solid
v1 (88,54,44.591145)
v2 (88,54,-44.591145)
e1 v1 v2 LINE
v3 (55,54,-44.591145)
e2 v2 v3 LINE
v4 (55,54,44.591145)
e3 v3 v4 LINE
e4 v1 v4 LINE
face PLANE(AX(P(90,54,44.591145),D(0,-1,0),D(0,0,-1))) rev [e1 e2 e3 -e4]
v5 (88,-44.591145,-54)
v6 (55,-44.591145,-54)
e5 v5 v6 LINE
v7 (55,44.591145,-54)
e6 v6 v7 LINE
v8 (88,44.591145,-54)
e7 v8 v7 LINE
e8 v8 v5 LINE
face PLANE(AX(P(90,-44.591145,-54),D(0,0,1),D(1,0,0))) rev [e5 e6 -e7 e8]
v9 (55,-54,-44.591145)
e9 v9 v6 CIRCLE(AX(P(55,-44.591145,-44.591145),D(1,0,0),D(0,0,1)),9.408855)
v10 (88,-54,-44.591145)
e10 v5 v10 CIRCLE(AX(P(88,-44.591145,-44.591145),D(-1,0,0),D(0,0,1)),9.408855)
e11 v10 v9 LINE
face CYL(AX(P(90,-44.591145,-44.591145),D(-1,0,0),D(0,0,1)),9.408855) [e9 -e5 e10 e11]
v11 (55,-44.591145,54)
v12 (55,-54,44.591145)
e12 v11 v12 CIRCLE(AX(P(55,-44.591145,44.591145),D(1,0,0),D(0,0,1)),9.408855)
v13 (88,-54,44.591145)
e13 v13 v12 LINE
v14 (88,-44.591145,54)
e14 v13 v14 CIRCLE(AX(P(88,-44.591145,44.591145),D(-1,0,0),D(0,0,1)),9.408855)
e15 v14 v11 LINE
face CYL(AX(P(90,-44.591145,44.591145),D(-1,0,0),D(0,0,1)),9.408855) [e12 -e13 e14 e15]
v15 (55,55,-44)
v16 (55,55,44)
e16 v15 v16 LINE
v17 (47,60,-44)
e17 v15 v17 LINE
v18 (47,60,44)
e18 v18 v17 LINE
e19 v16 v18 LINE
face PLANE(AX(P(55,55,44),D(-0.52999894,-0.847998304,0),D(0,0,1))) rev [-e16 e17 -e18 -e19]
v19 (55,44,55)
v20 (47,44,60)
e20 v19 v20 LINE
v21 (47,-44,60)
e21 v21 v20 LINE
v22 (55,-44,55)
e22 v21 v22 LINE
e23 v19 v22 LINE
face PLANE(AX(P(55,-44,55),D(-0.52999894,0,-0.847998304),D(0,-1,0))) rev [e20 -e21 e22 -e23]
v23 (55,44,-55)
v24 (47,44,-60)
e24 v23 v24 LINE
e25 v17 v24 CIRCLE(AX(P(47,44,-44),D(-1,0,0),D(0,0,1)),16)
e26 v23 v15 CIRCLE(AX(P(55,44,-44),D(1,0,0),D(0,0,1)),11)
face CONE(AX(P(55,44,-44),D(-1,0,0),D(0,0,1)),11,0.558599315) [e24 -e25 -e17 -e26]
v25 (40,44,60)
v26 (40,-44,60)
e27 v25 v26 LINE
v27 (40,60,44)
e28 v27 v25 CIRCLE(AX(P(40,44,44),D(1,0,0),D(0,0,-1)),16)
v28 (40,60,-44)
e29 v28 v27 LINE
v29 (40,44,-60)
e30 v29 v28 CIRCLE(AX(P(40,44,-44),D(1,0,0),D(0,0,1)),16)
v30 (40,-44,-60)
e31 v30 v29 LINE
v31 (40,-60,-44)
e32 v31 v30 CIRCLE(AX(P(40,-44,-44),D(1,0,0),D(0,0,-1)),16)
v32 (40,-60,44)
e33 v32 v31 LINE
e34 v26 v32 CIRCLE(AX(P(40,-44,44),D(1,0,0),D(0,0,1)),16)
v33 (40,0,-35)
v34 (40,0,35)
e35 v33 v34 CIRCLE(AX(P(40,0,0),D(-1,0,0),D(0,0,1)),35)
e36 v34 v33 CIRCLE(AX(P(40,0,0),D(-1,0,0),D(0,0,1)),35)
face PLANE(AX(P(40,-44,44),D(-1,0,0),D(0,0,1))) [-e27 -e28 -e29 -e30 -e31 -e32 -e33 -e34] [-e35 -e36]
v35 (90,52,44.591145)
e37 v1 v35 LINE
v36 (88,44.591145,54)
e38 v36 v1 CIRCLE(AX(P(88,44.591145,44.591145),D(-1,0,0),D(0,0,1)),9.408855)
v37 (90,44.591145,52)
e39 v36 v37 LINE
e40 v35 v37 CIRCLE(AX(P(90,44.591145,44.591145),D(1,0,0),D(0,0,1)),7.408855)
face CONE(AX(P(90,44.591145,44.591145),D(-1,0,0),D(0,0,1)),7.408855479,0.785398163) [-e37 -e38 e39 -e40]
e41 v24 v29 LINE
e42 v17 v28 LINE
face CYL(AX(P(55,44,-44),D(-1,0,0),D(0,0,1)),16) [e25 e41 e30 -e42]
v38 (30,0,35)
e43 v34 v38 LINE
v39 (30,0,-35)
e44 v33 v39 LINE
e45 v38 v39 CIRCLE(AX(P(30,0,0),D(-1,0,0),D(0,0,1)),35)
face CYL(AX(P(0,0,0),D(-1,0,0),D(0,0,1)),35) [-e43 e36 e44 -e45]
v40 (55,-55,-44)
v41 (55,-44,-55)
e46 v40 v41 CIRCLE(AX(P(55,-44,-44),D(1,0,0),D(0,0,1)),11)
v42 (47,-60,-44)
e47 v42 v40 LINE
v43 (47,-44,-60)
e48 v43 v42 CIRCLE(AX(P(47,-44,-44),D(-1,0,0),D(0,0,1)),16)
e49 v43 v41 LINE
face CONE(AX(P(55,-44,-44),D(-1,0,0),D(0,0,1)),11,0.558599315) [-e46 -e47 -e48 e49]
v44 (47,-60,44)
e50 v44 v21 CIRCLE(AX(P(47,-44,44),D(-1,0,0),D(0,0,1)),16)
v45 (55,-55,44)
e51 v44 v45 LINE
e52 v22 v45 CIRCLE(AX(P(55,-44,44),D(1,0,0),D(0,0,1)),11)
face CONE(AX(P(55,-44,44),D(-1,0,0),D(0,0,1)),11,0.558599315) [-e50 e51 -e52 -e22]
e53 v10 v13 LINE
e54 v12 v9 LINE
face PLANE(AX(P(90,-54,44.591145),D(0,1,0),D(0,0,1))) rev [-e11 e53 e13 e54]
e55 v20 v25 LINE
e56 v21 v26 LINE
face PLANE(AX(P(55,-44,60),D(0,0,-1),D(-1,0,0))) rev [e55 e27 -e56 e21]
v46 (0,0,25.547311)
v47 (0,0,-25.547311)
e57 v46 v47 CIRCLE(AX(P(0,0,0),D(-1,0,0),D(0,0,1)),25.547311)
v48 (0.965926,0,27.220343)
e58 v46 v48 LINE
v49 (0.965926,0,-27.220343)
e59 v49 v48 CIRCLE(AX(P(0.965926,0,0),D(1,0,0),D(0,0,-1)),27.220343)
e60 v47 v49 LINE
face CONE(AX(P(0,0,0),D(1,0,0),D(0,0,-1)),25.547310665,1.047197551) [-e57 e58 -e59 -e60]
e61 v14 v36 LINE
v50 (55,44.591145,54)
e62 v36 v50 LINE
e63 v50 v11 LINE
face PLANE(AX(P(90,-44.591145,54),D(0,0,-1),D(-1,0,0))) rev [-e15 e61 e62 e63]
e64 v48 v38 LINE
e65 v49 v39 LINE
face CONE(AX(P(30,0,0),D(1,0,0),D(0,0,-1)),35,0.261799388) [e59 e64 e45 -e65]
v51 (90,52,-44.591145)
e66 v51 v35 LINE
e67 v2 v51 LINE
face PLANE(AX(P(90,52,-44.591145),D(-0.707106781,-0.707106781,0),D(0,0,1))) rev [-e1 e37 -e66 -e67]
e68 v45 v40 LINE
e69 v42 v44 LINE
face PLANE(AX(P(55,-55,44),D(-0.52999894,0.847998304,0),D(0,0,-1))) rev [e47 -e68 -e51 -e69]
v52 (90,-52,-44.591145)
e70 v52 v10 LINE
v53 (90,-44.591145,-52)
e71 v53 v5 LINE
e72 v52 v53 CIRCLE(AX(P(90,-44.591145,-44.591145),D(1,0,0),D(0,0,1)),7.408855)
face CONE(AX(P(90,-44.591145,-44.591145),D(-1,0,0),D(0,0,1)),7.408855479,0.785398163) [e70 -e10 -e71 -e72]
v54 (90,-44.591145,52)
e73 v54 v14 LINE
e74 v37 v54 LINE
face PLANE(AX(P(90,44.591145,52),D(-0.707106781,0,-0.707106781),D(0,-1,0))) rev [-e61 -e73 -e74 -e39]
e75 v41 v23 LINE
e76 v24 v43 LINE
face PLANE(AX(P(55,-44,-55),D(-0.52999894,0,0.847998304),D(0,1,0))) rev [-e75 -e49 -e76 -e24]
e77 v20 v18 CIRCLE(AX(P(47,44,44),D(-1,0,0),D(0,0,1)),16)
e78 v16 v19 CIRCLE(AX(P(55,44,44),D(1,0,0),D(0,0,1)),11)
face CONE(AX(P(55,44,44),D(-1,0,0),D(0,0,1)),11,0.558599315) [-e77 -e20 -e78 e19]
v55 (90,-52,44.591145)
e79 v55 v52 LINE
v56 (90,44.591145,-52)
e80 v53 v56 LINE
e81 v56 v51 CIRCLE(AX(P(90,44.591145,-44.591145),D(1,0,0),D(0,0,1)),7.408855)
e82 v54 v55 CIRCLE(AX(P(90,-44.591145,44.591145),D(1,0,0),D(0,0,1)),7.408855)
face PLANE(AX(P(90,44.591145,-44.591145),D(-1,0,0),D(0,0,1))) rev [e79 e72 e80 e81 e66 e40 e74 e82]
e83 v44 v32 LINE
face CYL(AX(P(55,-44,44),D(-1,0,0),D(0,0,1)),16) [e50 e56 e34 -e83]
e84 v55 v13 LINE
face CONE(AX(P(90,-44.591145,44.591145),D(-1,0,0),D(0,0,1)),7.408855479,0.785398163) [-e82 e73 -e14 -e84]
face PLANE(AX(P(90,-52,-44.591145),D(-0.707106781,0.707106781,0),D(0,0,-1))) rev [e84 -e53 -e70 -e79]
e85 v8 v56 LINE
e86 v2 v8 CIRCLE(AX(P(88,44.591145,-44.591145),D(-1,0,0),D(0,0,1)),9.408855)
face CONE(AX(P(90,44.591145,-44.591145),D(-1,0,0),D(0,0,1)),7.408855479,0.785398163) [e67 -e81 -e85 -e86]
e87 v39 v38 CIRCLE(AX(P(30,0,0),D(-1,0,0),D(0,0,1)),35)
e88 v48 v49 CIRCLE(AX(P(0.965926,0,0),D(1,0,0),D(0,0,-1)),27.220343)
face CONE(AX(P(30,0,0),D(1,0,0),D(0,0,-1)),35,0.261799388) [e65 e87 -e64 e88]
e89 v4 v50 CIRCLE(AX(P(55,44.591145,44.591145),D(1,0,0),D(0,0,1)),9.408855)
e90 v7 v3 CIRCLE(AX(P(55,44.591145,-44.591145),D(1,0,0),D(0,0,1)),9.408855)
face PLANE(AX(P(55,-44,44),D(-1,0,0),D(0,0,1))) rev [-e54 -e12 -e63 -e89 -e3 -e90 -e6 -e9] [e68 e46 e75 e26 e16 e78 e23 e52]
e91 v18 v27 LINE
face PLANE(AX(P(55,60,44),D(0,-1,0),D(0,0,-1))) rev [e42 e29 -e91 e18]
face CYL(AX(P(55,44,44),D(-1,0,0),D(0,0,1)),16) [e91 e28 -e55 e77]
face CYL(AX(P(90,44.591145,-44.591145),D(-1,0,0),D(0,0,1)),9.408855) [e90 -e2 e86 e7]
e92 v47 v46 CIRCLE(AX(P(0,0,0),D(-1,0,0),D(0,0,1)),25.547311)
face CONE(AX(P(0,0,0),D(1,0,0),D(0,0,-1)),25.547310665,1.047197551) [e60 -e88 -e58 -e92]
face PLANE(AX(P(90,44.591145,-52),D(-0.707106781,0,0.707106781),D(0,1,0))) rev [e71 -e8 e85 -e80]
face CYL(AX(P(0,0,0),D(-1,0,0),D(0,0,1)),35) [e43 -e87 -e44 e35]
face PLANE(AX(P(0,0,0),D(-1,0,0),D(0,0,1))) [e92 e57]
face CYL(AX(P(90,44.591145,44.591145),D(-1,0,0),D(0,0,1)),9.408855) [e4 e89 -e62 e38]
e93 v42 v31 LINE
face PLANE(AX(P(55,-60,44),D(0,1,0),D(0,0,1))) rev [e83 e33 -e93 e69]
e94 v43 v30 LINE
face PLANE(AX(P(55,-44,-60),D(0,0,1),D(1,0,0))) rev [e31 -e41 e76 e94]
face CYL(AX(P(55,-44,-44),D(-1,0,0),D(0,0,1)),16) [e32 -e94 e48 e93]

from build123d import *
from OCP.BRepFilletAPI import BRepFilletAPI_MakeChamfer

# Parameters (mm, degrees)
SKETCH1_W           = 10
SKETCH1_H           = 35
BOSS_EXTRUDE1_DEPTH = 15
CHAMFER1_SIZE       = 8
CHAMFER1_SIZE2      = 5
BOSS_EXTRUDE2_DEPTH = 35
CHAMFER2_SIZE       = 2
CHAMFER3_SIZE       = 1
CHAMFER3_SIZE2      = 1.414213562


with BuildPart() as part:
    # Sketch1 → Revolve1 (revolve)
    with BuildSketch(Plane(origin=(0, 0, 0), x_dir=(1, 0, 0), z_dir=(0, 1, 0)), mode=Mode.PRIVATE) as revolve1_sk:
        with Locations((35, 17.5)):
            Rectangle(SKETCH1_W, SKETCH1_H)
        Polygon((0, 0), (30, 0), (30, 35), (0, 26.961524227), align=None)
    revolve(revolve1_sk.sketch.rotate(Axis((0, 0, 0), (1, 0, 0)), 180), axis=Axis((0, 0, 0), (1, 0, 0)))

    # Sketch2 → Boss-Extrude1 (add)
    with BuildSketch(Plane(origin=(40, 0, 0), x_dir=(0, 0, -1), z_dir=(1, 0, 0))):
        with BuildLine():
            Line((-44, -60), (44, -60))
            ThreePointArc((44, -60), (55.313708499, -55.313708499), (60, -44))
            Line((60, -44), (60, 44))
            ThreePointArc((60, 44), (55.313708499, 55.313708499), (44, 60))
            Line((44, 60), (-44, 60))
            ThreePointArc((-44, 60), (-55.313708499, 55.313708499), (-60, 44))
            Line((-60, 44), (-60, -44))
            ThreePointArc((-60, -44), (-55.313708499, -55.313708499), (-44, -60))
        make_face()
    extrude(amount=BOSS_EXTRUDE1_DEPTH)

    # Chamfer1: one chamfer whose edges measure the first distance from different faces: ONE call of the kernel's chamfer builder (chamfer() names one face for all edges)
    chamfer1_edges_1 = [part.edges().sort_by_distance(p)[0] for p in [
        (55, -55.313708499, 55.313708499),
    ]]
    chamfer1_side_1 = [part.faces().sort_by_distance(p)[0] for p in [
        (47.5, -55.313708499, 55.313708499),
    ]]
    chamfer1_edges_2 = [part.edges().sort_by_distance(p)[0] for p in [
        (55, -60, 0),
    ]]
    chamfer1_side_2 = [part.faces().sort_by_distance(p)[0] for p in [
        (47.5, -60, 0),
    ]]
    chamfer1_edges_3 = [part.edges().sort_by_distance(p)[0] for p in [
        (55, -55.313708499, -55.313708499),
    ]]
    chamfer1_side_3 = [part.faces().sort_by_distance(p)[0] for p in [
        (47.5, -55.313708499, -55.313708499),
    ]]
    chamfer1_edges_4 = [part.edges().sort_by_distance(p)[0] for p in [
        (55, 0, -60),
    ]]
    chamfer1_side_4 = [part.faces().sort_by_distance(p)[0] for p in [
        (47.5, 0, -60),
    ]]
    chamfer1_edges_5 = [part.edges().sort_by_distance(p)[0] for p in [
        (55, 55.313708499, -55.313708499),
    ]]
    chamfer1_side_5 = [part.faces().sort_by_distance(p)[0] for p in [
        (47.5, 55.313708499, -55.313708499),
    ]]
    chamfer1_edges_6 = [part.edges().sort_by_distance(p)[0] for p in [
        (55, 60, 0),
    ]]
    chamfer1_side_6 = [part.faces().sort_by_distance(p)[0] for p in [
        (47.5, 60, 0),
    ]]
    chamfer1_edges_7 = [part.edges().sort_by_distance(p)[0] for p in [
        (55, 55.313708499, 55.313708499),
    ]]
    chamfer1_side_7 = [part.faces().sort_by_distance(p)[0] for p in [
        (47.5, 55.313708499, 55.313708499),
    ]]
    chamfer1_edges_8 = [part.edges().sort_by_distance(p)[0] for p in [
        (55, 0, 60),
    ]]
    chamfer1_side_8 = [part.faces().sort_by_distance(p)[0] for p in [
        (47.5, 0, 60),
    ]]
    chamfer1 = BRepFilletAPI_MakeChamfer(part.part.solid().wrapped)
    for e in chamfer1_edges_1:
        chamfer1.Add(CHAMFER1_SIZE, CHAMFER1_SIZE2, e.wrapped, chamfer1_side_1[0].wrapped)  # the first distance lies on this face
    for e in chamfer1_edges_2:
        chamfer1.Add(CHAMFER1_SIZE, CHAMFER1_SIZE2, e.wrapped, chamfer1_side_2[0].wrapped)  # the first distance lies on this face
    for e in chamfer1_edges_3:
        chamfer1.Add(CHAMFER1_SIZE, CHAMFER1_SIZE2, e.wrapped, chamfer1_side_3[0].wrapped)  # the first distance lies on this face
    for e in chamfer1_edges_4:
        chamfer1.Add(CHAMFER1_SIZE, CHAMFER1_SIZE2, e.wrapped, chamfer1_side_4[0].wrapped)  # the first distance lies on this face
    for e in chamfer1_edges_5:
        chamfer1.Add(CHAMFER1_SIZE, CHAMFER1_SIZE2, e.wrapped, chamfer1_side_5[0].wrapped)  # the first distance lies on this face
    for e in chamfer1_edges_6:
        chamfer1.Add(CHAMFER1_SIZE, CHAMFER1_SIZE2, e.wrapped, chamfer1_side_6[0].wrapped)  # the first distance lies on this face
    for e in chamfer1_edges_7:
        chamfer1.Add(CHAMFER1_SIZE, CHAMFER1_SIZE2, e.wrapped, chamfer1_side_7[0].wrapped)  # the first distance lies on this face
    for e in chamfer1_edges_8:
        chamfer1.Add(CHAMFER1_SIZE, CHAMFER1_SIZE2, e.wrapped, chamfer1_side_8[0].wrapped)  # the first distance lies on this face
    add(Compound.cast(chamfer1.Shape()), mode=Mode.REPLACE)

    # Sketch3 → Boss-Extrude2 (add)
    with BuildSketch(Plane(origin=(55, 0, 0), x_dir=(0, 0, -1), z_dir=(1, 0, 0))):
        with BuildLine():
            Line((-44.591144521, -54), (44.591144521, -54))
            ThreePointArc((44.591144521, -54), (51.244210033, -51.244210033), (54, -44.591144521))
            Line((54, -44.591144521), (54, 44.591144521))
            ThreePointArc((54, 44.591144521), (51.244210033, 51.244210033), (44.591144521, 54))
            Line((44.591144521, 54), (-44.591144521, 54))
            ThreePointArc((-44.591144521, 54), (-51.244210033, 51.244210033), (-54, 44.591144521))
            Line((-54, 44.591144521), (-54, -44.591144521))
            ThreePointArc((-54, -44.591144521), (-51.244210033, -51.244210033), (-44.591144521, -54))
        make_face()
    extrude(amount=BOSS_EXTRUDE2_DEPTH)

    # Chamfer2
    chamfer2_edges = [part.edges().sort_by_distance(p)[0] for p in [
        (90, 51.244210033, -51.244210033),
        (90, 54, 0),
        (90, 51.244210033, 51.244210033),
        (90, 0, 54),
        (90, -51.244210033, 51.244210033),
        (90, -54, 0),
        (90, -51.244210033, -51.244210033),
        (90, 0, -54),
    ]]
    chamfer(chamfer2_edges, length=CHAMFER2_SIZE)

    # Chamfer3
    chamfer3_edges = [part.edges().sort_by_distance(p)[0] for p in [
        (0, 0, -26.961524227),
    ]]
    chamfer3_side = [part.faces().sort_by_distance(p)[0] for p in [
        (15, 0, -30.980762114),
    ]]
    chamfer(chamfer3_edges, length=CHAMFER3_SIZE, length2=CHAMFER3_SIZE2, reference=chamfer3_side[0])


solid = part.part
